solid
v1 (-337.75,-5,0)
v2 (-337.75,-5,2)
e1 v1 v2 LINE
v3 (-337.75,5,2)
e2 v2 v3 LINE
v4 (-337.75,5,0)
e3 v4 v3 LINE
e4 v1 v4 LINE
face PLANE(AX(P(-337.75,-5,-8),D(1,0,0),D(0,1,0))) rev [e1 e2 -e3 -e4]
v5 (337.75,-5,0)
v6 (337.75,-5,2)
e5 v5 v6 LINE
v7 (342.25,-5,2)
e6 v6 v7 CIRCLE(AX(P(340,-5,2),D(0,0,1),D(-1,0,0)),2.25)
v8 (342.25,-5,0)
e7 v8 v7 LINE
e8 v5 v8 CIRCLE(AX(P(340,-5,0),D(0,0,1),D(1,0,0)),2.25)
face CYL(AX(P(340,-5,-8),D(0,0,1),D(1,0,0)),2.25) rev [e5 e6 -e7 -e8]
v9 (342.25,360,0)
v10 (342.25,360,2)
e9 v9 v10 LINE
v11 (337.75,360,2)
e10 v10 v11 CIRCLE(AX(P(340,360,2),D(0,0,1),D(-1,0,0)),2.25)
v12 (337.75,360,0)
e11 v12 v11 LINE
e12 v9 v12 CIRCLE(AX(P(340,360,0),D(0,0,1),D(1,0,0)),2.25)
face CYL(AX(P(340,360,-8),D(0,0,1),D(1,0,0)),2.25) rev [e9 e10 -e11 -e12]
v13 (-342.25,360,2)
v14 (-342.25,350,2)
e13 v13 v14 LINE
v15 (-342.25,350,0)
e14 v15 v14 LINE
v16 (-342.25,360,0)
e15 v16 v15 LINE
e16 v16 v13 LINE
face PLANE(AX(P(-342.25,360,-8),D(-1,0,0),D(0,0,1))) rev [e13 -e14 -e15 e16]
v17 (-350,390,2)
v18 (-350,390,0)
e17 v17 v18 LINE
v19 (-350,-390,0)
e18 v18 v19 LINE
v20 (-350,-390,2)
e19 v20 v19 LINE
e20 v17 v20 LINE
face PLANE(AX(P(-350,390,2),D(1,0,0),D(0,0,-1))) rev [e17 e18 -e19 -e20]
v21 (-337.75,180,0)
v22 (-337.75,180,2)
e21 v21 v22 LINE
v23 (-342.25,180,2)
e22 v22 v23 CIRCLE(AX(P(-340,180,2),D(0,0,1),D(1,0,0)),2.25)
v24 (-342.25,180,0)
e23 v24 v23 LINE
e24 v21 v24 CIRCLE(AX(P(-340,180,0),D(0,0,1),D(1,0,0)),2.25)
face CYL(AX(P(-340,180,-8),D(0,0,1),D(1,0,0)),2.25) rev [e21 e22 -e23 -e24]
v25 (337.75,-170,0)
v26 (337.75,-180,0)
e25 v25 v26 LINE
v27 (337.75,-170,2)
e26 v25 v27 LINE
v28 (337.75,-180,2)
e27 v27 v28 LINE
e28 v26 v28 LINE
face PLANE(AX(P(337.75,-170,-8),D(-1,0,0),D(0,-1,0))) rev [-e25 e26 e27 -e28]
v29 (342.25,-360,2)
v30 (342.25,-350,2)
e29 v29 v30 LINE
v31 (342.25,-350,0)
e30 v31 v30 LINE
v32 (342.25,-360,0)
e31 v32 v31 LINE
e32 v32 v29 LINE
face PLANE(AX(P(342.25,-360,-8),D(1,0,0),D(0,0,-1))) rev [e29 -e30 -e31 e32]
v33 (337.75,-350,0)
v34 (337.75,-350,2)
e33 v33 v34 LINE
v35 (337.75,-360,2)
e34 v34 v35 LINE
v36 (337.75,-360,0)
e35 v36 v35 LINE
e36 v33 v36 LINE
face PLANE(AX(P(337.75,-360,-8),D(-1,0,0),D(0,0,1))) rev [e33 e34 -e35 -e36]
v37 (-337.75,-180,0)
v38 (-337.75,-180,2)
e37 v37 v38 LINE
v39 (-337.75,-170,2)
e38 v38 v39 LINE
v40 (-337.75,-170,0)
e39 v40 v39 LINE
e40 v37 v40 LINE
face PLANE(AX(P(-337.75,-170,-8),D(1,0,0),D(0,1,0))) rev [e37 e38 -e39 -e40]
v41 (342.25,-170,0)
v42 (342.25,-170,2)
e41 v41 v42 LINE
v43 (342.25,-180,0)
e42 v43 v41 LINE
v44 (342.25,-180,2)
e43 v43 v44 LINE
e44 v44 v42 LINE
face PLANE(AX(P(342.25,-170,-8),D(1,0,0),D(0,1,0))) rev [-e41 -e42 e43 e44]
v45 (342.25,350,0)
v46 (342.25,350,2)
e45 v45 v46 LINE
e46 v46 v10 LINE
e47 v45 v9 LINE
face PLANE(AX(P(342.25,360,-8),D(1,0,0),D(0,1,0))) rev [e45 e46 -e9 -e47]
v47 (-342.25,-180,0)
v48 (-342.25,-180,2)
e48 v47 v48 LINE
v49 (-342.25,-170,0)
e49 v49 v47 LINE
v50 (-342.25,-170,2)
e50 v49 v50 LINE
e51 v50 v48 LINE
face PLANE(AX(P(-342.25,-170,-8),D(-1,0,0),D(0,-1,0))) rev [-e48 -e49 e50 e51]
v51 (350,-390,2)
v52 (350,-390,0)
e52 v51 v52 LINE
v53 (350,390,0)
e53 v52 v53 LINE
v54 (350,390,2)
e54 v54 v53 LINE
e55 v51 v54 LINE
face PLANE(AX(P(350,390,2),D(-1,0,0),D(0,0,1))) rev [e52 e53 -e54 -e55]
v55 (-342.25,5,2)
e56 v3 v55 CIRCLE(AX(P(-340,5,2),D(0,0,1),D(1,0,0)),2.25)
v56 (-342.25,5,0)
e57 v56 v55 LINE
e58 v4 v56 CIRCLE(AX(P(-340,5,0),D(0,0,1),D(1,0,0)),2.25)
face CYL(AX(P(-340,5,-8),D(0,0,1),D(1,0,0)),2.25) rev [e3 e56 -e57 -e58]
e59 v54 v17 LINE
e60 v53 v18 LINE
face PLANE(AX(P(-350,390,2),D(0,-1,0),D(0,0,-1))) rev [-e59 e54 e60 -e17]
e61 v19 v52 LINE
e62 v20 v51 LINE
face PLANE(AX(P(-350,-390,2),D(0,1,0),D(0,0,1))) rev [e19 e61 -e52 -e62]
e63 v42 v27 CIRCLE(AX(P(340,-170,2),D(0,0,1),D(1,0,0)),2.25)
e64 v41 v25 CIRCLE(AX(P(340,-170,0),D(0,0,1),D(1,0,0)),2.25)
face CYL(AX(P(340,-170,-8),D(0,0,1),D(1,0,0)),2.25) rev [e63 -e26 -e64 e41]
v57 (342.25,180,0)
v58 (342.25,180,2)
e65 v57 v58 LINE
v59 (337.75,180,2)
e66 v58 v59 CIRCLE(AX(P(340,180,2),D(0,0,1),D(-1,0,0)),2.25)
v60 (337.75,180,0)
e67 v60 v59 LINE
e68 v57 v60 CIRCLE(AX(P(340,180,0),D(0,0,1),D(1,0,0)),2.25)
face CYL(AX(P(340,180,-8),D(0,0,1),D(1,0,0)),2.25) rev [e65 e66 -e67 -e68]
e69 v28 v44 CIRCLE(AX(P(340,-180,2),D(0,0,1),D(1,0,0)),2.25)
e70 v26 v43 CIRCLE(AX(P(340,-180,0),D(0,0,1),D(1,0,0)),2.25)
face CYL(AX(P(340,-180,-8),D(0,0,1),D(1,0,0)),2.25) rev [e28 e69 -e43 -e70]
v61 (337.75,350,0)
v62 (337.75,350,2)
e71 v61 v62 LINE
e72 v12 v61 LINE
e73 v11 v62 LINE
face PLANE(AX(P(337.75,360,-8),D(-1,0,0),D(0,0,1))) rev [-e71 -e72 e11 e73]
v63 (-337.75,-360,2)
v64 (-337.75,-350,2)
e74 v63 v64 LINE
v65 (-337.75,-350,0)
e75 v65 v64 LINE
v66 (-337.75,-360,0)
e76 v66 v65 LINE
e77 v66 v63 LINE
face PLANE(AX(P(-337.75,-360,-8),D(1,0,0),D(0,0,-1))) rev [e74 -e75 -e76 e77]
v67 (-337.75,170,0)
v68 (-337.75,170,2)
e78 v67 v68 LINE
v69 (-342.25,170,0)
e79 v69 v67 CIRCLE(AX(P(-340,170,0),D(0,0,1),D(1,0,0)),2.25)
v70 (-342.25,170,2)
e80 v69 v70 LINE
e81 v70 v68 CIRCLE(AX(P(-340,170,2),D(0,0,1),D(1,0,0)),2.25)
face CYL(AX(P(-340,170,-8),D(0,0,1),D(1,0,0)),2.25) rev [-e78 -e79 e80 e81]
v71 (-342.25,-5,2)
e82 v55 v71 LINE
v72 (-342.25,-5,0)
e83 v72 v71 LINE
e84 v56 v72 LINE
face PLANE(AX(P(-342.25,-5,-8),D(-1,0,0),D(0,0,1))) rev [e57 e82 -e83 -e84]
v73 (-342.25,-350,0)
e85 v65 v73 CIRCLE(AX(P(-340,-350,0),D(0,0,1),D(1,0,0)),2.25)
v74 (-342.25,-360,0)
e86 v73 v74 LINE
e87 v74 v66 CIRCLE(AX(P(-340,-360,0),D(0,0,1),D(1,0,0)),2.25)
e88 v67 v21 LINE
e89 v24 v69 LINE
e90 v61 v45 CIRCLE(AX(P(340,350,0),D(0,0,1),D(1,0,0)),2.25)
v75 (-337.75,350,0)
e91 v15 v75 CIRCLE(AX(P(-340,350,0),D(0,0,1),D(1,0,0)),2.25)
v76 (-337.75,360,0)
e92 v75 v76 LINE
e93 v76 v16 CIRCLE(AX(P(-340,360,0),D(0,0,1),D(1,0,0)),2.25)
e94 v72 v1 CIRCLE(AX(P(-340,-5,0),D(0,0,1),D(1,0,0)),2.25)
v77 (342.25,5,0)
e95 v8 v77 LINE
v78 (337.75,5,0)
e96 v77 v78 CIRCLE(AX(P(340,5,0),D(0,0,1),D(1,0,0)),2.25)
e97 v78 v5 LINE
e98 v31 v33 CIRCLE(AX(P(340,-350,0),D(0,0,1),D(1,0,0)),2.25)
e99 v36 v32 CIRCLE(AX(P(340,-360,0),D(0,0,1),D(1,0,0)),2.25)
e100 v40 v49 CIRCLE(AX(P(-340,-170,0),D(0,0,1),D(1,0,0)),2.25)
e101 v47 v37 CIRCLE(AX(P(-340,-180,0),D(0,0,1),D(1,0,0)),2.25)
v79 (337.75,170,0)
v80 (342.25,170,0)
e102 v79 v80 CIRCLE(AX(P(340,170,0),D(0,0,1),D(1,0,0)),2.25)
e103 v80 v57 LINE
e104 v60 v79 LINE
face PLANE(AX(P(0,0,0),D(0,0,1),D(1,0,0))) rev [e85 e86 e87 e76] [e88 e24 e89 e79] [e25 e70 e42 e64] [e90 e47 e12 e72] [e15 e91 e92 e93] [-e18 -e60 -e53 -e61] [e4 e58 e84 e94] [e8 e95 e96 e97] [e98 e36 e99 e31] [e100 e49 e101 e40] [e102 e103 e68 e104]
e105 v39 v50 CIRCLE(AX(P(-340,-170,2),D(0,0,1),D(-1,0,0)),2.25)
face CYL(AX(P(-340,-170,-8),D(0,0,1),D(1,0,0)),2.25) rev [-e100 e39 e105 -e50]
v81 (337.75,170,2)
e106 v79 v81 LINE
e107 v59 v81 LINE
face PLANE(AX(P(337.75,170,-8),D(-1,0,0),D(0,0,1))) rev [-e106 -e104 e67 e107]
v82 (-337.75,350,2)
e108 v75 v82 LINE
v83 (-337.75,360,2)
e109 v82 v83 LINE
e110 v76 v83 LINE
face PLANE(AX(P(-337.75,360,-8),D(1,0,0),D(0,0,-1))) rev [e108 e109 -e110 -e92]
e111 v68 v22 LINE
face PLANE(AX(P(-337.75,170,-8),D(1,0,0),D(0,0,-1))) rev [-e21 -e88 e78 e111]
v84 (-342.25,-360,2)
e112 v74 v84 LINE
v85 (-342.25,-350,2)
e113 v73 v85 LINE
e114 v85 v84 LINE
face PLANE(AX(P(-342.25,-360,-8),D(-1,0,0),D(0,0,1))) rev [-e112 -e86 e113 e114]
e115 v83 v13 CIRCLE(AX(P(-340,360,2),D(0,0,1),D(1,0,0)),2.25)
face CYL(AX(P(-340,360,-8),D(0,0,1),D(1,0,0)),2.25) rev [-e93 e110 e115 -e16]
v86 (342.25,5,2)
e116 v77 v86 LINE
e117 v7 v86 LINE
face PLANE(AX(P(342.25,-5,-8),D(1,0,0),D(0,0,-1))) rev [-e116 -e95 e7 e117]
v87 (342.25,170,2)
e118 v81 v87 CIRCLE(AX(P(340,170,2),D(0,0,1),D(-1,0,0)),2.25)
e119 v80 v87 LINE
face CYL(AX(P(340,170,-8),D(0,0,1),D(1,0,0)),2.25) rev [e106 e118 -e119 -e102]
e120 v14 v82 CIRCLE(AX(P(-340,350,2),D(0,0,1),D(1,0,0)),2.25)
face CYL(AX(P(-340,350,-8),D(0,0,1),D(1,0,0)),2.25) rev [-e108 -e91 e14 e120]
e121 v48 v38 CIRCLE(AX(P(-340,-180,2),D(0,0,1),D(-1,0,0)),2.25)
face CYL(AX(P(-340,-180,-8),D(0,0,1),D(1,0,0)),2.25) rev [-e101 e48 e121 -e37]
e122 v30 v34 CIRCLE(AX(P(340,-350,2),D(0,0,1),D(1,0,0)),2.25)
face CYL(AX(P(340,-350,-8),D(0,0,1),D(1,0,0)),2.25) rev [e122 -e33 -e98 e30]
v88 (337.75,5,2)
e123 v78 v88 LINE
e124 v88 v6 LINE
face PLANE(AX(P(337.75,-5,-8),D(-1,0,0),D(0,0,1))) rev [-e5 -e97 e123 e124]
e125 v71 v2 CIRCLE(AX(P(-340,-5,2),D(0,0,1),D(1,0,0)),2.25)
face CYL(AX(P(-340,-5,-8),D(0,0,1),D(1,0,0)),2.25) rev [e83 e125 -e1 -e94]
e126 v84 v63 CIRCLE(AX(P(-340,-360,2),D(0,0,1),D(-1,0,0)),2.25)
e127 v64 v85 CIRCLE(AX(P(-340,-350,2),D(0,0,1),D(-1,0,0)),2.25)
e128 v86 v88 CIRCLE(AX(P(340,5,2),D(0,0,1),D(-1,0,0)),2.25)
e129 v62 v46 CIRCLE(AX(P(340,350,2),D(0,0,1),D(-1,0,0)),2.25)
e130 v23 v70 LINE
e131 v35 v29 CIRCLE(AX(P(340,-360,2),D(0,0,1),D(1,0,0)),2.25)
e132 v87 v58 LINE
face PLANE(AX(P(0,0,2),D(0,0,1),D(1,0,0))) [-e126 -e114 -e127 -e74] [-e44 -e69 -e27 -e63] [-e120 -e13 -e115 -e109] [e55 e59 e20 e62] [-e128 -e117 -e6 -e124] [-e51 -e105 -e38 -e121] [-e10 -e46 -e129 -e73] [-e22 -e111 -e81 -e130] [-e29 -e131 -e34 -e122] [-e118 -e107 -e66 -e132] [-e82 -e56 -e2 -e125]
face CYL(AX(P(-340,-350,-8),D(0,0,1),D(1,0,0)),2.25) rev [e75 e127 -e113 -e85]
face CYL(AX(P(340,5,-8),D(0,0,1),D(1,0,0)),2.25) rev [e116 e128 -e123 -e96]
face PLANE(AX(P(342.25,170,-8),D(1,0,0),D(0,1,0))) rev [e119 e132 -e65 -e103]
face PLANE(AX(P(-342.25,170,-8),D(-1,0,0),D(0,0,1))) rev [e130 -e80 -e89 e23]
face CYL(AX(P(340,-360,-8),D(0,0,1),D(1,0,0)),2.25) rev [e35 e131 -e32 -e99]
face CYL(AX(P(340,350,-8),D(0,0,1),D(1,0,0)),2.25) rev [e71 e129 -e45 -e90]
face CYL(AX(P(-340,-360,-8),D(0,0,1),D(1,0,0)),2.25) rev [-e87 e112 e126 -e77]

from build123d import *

# Parameters (mm, degrees)
SKETCH_1_W          = 700
SKETCH_1_H          = 780
EXTRUDE_1_DEPTH     = 2
CUT_EXTRUDE_1_DEPTH = 10


with BuildPart() as part:
    # 草图1 → 凸台-拉伸1 (new body)
    with BuildSketch(Plane.XY):
        Rectangle(SKETCH_1_W, SKETCH_1_H)
    extrude(amount=EXTRUDE_1_DEPTH)

    # 草图2 → 切除-拉伸1 (cut)
    with BuildSketch(Plane.XY.offset(2)):
        with BuildLine():
            Line((-337.75, 360), (-337.75, 350))
            ThreePointArc((-337.75, 350), (-340, 347.75), (-342.25, 350))
            Line((-342.25, 350), (-342.25, 360))
            ThreePointArc((-342.25, 360), (-340, 362.25), (-337.75, 360))
        make_face()
        with BuildLine():
            Line((337.75, 360), (337.75, 350))
            ThreePointArc((337.75, 350), (340, 347.75), (342.25, 350))
            Line((342.25, 350), (342.25, 360))
            ThreePointArc((342.25, 360), (340, 362.25), (337.75, 360))
        make_face()
        with BuildLine():
            Line((-342.25, 170), (-342.25, 180))
            ThreePointArc((-342.25, 180), (-340, 182.25), (-337.75, 180))
            Line((-337.75, 180), (-337.75, 170))
            ThreePointArc((-337.75, 170), (-340, 167.75), (-342.25, 170))
        make_face()
        with BuildLine():
            Line((-342.25, -5), (-342.25, 5))
            ThreePointArc((-342.25, 5), (-340, 7.25), (-337.75, 5))
            Line((-337.75, 5), (-337.75, -5))
            ThreePointArc((-337.75, -5), (-340, -7.25), (-342.25, -5))
        make_face()
        with BuildLine():
            Line((342.25, 170), (342.25, 180))
            ThreePointArc((342.25, 180), (340, 182.25), (337.75, 180))
            Line((337.75, 180), (337.75, 170))
            ThreePointArc((337.75, 170), (340, 167.75), (342.25, 170))
        make_face()
        with BuildLine():
            Line((342.25, -5), (342.25, 5))
            ThreePointArc((342.25, 5), (340, 7.25), (337.75, 5))
            Line((337.75, 5), (337.75, -5))
            ThreePointArc((337.75, -5), (340, -7.25), (342.25, -5))
        make_face()
        with BuildLine():
            Line((-342.25, 540), (-342.25, 530))
            ThreePointArc((-342.25, 530), (-340, 527.75), (-337.75, 530))
            Line((-337.75, 530), (-337.75, 540))
            ThreePointArc((-337.75, 540), (-340, 542.25), (-342.25, 540))
        make_face()
        with BuildLine():
            Line((342.25, 540), (342.25, 530))
            ThreePointArc((342.25, 530), (340, 527.75), (337.75, 530))
            Line((337.75, 530), (337.75, 540))
            ThreePointArc((337.75, 540), (340, 542.25), (342.25, 540))
        make_face()
        with BuildLine():
            Line((342.25, -170), (342.25, -180))
            ThreePointArc((342.25, -180), (340, -182.25), (337.75, -180))
            Line((337.75, -180), (337.75, -170))
            ThreePointArc((337.75, -170), (340, -167.75), (342.25, -170))
        make_face()
        with BuildLine():
            Line((-342.25, -170), (-342.25, -180))
            ThreePointArc((-342.25, -180), (-340, -182.25), (-337.75, -180))
            Line((-337.75, -180), (-337.75, -170))
            ThreePointArc((-337.75, -170), (-340, -167.75), (-342.25, -170))
        make_face()
        with BuildLine():
            Line((337.75, -360), (337.75, -350))
            ThreePointArc((337.75, -350), (340, -347.75), (342.25, -350))
            Line((342.25, -350), (342.25, -360))
            ThreePointArc((342.25, -360), (340, -362.25), (337.75, -360))
        make_face()
        with BuildLine():
            Line((-337.75, -360), (-337.75, -350))
            ThreePointArc((-337.75, -350), (-340, -347.75), (-342.25, -350))
            Line((-342.25, -350), (-342.25, -360))
            ThreePointArc((-342.25, -360), (-340, -362.25), (-337.75, -360))
        make_face()
    extrude(amount=-CUT_EXTRUDE_1_DEPTH, mode=Mode.SUBTRACT)


solid = part.part
